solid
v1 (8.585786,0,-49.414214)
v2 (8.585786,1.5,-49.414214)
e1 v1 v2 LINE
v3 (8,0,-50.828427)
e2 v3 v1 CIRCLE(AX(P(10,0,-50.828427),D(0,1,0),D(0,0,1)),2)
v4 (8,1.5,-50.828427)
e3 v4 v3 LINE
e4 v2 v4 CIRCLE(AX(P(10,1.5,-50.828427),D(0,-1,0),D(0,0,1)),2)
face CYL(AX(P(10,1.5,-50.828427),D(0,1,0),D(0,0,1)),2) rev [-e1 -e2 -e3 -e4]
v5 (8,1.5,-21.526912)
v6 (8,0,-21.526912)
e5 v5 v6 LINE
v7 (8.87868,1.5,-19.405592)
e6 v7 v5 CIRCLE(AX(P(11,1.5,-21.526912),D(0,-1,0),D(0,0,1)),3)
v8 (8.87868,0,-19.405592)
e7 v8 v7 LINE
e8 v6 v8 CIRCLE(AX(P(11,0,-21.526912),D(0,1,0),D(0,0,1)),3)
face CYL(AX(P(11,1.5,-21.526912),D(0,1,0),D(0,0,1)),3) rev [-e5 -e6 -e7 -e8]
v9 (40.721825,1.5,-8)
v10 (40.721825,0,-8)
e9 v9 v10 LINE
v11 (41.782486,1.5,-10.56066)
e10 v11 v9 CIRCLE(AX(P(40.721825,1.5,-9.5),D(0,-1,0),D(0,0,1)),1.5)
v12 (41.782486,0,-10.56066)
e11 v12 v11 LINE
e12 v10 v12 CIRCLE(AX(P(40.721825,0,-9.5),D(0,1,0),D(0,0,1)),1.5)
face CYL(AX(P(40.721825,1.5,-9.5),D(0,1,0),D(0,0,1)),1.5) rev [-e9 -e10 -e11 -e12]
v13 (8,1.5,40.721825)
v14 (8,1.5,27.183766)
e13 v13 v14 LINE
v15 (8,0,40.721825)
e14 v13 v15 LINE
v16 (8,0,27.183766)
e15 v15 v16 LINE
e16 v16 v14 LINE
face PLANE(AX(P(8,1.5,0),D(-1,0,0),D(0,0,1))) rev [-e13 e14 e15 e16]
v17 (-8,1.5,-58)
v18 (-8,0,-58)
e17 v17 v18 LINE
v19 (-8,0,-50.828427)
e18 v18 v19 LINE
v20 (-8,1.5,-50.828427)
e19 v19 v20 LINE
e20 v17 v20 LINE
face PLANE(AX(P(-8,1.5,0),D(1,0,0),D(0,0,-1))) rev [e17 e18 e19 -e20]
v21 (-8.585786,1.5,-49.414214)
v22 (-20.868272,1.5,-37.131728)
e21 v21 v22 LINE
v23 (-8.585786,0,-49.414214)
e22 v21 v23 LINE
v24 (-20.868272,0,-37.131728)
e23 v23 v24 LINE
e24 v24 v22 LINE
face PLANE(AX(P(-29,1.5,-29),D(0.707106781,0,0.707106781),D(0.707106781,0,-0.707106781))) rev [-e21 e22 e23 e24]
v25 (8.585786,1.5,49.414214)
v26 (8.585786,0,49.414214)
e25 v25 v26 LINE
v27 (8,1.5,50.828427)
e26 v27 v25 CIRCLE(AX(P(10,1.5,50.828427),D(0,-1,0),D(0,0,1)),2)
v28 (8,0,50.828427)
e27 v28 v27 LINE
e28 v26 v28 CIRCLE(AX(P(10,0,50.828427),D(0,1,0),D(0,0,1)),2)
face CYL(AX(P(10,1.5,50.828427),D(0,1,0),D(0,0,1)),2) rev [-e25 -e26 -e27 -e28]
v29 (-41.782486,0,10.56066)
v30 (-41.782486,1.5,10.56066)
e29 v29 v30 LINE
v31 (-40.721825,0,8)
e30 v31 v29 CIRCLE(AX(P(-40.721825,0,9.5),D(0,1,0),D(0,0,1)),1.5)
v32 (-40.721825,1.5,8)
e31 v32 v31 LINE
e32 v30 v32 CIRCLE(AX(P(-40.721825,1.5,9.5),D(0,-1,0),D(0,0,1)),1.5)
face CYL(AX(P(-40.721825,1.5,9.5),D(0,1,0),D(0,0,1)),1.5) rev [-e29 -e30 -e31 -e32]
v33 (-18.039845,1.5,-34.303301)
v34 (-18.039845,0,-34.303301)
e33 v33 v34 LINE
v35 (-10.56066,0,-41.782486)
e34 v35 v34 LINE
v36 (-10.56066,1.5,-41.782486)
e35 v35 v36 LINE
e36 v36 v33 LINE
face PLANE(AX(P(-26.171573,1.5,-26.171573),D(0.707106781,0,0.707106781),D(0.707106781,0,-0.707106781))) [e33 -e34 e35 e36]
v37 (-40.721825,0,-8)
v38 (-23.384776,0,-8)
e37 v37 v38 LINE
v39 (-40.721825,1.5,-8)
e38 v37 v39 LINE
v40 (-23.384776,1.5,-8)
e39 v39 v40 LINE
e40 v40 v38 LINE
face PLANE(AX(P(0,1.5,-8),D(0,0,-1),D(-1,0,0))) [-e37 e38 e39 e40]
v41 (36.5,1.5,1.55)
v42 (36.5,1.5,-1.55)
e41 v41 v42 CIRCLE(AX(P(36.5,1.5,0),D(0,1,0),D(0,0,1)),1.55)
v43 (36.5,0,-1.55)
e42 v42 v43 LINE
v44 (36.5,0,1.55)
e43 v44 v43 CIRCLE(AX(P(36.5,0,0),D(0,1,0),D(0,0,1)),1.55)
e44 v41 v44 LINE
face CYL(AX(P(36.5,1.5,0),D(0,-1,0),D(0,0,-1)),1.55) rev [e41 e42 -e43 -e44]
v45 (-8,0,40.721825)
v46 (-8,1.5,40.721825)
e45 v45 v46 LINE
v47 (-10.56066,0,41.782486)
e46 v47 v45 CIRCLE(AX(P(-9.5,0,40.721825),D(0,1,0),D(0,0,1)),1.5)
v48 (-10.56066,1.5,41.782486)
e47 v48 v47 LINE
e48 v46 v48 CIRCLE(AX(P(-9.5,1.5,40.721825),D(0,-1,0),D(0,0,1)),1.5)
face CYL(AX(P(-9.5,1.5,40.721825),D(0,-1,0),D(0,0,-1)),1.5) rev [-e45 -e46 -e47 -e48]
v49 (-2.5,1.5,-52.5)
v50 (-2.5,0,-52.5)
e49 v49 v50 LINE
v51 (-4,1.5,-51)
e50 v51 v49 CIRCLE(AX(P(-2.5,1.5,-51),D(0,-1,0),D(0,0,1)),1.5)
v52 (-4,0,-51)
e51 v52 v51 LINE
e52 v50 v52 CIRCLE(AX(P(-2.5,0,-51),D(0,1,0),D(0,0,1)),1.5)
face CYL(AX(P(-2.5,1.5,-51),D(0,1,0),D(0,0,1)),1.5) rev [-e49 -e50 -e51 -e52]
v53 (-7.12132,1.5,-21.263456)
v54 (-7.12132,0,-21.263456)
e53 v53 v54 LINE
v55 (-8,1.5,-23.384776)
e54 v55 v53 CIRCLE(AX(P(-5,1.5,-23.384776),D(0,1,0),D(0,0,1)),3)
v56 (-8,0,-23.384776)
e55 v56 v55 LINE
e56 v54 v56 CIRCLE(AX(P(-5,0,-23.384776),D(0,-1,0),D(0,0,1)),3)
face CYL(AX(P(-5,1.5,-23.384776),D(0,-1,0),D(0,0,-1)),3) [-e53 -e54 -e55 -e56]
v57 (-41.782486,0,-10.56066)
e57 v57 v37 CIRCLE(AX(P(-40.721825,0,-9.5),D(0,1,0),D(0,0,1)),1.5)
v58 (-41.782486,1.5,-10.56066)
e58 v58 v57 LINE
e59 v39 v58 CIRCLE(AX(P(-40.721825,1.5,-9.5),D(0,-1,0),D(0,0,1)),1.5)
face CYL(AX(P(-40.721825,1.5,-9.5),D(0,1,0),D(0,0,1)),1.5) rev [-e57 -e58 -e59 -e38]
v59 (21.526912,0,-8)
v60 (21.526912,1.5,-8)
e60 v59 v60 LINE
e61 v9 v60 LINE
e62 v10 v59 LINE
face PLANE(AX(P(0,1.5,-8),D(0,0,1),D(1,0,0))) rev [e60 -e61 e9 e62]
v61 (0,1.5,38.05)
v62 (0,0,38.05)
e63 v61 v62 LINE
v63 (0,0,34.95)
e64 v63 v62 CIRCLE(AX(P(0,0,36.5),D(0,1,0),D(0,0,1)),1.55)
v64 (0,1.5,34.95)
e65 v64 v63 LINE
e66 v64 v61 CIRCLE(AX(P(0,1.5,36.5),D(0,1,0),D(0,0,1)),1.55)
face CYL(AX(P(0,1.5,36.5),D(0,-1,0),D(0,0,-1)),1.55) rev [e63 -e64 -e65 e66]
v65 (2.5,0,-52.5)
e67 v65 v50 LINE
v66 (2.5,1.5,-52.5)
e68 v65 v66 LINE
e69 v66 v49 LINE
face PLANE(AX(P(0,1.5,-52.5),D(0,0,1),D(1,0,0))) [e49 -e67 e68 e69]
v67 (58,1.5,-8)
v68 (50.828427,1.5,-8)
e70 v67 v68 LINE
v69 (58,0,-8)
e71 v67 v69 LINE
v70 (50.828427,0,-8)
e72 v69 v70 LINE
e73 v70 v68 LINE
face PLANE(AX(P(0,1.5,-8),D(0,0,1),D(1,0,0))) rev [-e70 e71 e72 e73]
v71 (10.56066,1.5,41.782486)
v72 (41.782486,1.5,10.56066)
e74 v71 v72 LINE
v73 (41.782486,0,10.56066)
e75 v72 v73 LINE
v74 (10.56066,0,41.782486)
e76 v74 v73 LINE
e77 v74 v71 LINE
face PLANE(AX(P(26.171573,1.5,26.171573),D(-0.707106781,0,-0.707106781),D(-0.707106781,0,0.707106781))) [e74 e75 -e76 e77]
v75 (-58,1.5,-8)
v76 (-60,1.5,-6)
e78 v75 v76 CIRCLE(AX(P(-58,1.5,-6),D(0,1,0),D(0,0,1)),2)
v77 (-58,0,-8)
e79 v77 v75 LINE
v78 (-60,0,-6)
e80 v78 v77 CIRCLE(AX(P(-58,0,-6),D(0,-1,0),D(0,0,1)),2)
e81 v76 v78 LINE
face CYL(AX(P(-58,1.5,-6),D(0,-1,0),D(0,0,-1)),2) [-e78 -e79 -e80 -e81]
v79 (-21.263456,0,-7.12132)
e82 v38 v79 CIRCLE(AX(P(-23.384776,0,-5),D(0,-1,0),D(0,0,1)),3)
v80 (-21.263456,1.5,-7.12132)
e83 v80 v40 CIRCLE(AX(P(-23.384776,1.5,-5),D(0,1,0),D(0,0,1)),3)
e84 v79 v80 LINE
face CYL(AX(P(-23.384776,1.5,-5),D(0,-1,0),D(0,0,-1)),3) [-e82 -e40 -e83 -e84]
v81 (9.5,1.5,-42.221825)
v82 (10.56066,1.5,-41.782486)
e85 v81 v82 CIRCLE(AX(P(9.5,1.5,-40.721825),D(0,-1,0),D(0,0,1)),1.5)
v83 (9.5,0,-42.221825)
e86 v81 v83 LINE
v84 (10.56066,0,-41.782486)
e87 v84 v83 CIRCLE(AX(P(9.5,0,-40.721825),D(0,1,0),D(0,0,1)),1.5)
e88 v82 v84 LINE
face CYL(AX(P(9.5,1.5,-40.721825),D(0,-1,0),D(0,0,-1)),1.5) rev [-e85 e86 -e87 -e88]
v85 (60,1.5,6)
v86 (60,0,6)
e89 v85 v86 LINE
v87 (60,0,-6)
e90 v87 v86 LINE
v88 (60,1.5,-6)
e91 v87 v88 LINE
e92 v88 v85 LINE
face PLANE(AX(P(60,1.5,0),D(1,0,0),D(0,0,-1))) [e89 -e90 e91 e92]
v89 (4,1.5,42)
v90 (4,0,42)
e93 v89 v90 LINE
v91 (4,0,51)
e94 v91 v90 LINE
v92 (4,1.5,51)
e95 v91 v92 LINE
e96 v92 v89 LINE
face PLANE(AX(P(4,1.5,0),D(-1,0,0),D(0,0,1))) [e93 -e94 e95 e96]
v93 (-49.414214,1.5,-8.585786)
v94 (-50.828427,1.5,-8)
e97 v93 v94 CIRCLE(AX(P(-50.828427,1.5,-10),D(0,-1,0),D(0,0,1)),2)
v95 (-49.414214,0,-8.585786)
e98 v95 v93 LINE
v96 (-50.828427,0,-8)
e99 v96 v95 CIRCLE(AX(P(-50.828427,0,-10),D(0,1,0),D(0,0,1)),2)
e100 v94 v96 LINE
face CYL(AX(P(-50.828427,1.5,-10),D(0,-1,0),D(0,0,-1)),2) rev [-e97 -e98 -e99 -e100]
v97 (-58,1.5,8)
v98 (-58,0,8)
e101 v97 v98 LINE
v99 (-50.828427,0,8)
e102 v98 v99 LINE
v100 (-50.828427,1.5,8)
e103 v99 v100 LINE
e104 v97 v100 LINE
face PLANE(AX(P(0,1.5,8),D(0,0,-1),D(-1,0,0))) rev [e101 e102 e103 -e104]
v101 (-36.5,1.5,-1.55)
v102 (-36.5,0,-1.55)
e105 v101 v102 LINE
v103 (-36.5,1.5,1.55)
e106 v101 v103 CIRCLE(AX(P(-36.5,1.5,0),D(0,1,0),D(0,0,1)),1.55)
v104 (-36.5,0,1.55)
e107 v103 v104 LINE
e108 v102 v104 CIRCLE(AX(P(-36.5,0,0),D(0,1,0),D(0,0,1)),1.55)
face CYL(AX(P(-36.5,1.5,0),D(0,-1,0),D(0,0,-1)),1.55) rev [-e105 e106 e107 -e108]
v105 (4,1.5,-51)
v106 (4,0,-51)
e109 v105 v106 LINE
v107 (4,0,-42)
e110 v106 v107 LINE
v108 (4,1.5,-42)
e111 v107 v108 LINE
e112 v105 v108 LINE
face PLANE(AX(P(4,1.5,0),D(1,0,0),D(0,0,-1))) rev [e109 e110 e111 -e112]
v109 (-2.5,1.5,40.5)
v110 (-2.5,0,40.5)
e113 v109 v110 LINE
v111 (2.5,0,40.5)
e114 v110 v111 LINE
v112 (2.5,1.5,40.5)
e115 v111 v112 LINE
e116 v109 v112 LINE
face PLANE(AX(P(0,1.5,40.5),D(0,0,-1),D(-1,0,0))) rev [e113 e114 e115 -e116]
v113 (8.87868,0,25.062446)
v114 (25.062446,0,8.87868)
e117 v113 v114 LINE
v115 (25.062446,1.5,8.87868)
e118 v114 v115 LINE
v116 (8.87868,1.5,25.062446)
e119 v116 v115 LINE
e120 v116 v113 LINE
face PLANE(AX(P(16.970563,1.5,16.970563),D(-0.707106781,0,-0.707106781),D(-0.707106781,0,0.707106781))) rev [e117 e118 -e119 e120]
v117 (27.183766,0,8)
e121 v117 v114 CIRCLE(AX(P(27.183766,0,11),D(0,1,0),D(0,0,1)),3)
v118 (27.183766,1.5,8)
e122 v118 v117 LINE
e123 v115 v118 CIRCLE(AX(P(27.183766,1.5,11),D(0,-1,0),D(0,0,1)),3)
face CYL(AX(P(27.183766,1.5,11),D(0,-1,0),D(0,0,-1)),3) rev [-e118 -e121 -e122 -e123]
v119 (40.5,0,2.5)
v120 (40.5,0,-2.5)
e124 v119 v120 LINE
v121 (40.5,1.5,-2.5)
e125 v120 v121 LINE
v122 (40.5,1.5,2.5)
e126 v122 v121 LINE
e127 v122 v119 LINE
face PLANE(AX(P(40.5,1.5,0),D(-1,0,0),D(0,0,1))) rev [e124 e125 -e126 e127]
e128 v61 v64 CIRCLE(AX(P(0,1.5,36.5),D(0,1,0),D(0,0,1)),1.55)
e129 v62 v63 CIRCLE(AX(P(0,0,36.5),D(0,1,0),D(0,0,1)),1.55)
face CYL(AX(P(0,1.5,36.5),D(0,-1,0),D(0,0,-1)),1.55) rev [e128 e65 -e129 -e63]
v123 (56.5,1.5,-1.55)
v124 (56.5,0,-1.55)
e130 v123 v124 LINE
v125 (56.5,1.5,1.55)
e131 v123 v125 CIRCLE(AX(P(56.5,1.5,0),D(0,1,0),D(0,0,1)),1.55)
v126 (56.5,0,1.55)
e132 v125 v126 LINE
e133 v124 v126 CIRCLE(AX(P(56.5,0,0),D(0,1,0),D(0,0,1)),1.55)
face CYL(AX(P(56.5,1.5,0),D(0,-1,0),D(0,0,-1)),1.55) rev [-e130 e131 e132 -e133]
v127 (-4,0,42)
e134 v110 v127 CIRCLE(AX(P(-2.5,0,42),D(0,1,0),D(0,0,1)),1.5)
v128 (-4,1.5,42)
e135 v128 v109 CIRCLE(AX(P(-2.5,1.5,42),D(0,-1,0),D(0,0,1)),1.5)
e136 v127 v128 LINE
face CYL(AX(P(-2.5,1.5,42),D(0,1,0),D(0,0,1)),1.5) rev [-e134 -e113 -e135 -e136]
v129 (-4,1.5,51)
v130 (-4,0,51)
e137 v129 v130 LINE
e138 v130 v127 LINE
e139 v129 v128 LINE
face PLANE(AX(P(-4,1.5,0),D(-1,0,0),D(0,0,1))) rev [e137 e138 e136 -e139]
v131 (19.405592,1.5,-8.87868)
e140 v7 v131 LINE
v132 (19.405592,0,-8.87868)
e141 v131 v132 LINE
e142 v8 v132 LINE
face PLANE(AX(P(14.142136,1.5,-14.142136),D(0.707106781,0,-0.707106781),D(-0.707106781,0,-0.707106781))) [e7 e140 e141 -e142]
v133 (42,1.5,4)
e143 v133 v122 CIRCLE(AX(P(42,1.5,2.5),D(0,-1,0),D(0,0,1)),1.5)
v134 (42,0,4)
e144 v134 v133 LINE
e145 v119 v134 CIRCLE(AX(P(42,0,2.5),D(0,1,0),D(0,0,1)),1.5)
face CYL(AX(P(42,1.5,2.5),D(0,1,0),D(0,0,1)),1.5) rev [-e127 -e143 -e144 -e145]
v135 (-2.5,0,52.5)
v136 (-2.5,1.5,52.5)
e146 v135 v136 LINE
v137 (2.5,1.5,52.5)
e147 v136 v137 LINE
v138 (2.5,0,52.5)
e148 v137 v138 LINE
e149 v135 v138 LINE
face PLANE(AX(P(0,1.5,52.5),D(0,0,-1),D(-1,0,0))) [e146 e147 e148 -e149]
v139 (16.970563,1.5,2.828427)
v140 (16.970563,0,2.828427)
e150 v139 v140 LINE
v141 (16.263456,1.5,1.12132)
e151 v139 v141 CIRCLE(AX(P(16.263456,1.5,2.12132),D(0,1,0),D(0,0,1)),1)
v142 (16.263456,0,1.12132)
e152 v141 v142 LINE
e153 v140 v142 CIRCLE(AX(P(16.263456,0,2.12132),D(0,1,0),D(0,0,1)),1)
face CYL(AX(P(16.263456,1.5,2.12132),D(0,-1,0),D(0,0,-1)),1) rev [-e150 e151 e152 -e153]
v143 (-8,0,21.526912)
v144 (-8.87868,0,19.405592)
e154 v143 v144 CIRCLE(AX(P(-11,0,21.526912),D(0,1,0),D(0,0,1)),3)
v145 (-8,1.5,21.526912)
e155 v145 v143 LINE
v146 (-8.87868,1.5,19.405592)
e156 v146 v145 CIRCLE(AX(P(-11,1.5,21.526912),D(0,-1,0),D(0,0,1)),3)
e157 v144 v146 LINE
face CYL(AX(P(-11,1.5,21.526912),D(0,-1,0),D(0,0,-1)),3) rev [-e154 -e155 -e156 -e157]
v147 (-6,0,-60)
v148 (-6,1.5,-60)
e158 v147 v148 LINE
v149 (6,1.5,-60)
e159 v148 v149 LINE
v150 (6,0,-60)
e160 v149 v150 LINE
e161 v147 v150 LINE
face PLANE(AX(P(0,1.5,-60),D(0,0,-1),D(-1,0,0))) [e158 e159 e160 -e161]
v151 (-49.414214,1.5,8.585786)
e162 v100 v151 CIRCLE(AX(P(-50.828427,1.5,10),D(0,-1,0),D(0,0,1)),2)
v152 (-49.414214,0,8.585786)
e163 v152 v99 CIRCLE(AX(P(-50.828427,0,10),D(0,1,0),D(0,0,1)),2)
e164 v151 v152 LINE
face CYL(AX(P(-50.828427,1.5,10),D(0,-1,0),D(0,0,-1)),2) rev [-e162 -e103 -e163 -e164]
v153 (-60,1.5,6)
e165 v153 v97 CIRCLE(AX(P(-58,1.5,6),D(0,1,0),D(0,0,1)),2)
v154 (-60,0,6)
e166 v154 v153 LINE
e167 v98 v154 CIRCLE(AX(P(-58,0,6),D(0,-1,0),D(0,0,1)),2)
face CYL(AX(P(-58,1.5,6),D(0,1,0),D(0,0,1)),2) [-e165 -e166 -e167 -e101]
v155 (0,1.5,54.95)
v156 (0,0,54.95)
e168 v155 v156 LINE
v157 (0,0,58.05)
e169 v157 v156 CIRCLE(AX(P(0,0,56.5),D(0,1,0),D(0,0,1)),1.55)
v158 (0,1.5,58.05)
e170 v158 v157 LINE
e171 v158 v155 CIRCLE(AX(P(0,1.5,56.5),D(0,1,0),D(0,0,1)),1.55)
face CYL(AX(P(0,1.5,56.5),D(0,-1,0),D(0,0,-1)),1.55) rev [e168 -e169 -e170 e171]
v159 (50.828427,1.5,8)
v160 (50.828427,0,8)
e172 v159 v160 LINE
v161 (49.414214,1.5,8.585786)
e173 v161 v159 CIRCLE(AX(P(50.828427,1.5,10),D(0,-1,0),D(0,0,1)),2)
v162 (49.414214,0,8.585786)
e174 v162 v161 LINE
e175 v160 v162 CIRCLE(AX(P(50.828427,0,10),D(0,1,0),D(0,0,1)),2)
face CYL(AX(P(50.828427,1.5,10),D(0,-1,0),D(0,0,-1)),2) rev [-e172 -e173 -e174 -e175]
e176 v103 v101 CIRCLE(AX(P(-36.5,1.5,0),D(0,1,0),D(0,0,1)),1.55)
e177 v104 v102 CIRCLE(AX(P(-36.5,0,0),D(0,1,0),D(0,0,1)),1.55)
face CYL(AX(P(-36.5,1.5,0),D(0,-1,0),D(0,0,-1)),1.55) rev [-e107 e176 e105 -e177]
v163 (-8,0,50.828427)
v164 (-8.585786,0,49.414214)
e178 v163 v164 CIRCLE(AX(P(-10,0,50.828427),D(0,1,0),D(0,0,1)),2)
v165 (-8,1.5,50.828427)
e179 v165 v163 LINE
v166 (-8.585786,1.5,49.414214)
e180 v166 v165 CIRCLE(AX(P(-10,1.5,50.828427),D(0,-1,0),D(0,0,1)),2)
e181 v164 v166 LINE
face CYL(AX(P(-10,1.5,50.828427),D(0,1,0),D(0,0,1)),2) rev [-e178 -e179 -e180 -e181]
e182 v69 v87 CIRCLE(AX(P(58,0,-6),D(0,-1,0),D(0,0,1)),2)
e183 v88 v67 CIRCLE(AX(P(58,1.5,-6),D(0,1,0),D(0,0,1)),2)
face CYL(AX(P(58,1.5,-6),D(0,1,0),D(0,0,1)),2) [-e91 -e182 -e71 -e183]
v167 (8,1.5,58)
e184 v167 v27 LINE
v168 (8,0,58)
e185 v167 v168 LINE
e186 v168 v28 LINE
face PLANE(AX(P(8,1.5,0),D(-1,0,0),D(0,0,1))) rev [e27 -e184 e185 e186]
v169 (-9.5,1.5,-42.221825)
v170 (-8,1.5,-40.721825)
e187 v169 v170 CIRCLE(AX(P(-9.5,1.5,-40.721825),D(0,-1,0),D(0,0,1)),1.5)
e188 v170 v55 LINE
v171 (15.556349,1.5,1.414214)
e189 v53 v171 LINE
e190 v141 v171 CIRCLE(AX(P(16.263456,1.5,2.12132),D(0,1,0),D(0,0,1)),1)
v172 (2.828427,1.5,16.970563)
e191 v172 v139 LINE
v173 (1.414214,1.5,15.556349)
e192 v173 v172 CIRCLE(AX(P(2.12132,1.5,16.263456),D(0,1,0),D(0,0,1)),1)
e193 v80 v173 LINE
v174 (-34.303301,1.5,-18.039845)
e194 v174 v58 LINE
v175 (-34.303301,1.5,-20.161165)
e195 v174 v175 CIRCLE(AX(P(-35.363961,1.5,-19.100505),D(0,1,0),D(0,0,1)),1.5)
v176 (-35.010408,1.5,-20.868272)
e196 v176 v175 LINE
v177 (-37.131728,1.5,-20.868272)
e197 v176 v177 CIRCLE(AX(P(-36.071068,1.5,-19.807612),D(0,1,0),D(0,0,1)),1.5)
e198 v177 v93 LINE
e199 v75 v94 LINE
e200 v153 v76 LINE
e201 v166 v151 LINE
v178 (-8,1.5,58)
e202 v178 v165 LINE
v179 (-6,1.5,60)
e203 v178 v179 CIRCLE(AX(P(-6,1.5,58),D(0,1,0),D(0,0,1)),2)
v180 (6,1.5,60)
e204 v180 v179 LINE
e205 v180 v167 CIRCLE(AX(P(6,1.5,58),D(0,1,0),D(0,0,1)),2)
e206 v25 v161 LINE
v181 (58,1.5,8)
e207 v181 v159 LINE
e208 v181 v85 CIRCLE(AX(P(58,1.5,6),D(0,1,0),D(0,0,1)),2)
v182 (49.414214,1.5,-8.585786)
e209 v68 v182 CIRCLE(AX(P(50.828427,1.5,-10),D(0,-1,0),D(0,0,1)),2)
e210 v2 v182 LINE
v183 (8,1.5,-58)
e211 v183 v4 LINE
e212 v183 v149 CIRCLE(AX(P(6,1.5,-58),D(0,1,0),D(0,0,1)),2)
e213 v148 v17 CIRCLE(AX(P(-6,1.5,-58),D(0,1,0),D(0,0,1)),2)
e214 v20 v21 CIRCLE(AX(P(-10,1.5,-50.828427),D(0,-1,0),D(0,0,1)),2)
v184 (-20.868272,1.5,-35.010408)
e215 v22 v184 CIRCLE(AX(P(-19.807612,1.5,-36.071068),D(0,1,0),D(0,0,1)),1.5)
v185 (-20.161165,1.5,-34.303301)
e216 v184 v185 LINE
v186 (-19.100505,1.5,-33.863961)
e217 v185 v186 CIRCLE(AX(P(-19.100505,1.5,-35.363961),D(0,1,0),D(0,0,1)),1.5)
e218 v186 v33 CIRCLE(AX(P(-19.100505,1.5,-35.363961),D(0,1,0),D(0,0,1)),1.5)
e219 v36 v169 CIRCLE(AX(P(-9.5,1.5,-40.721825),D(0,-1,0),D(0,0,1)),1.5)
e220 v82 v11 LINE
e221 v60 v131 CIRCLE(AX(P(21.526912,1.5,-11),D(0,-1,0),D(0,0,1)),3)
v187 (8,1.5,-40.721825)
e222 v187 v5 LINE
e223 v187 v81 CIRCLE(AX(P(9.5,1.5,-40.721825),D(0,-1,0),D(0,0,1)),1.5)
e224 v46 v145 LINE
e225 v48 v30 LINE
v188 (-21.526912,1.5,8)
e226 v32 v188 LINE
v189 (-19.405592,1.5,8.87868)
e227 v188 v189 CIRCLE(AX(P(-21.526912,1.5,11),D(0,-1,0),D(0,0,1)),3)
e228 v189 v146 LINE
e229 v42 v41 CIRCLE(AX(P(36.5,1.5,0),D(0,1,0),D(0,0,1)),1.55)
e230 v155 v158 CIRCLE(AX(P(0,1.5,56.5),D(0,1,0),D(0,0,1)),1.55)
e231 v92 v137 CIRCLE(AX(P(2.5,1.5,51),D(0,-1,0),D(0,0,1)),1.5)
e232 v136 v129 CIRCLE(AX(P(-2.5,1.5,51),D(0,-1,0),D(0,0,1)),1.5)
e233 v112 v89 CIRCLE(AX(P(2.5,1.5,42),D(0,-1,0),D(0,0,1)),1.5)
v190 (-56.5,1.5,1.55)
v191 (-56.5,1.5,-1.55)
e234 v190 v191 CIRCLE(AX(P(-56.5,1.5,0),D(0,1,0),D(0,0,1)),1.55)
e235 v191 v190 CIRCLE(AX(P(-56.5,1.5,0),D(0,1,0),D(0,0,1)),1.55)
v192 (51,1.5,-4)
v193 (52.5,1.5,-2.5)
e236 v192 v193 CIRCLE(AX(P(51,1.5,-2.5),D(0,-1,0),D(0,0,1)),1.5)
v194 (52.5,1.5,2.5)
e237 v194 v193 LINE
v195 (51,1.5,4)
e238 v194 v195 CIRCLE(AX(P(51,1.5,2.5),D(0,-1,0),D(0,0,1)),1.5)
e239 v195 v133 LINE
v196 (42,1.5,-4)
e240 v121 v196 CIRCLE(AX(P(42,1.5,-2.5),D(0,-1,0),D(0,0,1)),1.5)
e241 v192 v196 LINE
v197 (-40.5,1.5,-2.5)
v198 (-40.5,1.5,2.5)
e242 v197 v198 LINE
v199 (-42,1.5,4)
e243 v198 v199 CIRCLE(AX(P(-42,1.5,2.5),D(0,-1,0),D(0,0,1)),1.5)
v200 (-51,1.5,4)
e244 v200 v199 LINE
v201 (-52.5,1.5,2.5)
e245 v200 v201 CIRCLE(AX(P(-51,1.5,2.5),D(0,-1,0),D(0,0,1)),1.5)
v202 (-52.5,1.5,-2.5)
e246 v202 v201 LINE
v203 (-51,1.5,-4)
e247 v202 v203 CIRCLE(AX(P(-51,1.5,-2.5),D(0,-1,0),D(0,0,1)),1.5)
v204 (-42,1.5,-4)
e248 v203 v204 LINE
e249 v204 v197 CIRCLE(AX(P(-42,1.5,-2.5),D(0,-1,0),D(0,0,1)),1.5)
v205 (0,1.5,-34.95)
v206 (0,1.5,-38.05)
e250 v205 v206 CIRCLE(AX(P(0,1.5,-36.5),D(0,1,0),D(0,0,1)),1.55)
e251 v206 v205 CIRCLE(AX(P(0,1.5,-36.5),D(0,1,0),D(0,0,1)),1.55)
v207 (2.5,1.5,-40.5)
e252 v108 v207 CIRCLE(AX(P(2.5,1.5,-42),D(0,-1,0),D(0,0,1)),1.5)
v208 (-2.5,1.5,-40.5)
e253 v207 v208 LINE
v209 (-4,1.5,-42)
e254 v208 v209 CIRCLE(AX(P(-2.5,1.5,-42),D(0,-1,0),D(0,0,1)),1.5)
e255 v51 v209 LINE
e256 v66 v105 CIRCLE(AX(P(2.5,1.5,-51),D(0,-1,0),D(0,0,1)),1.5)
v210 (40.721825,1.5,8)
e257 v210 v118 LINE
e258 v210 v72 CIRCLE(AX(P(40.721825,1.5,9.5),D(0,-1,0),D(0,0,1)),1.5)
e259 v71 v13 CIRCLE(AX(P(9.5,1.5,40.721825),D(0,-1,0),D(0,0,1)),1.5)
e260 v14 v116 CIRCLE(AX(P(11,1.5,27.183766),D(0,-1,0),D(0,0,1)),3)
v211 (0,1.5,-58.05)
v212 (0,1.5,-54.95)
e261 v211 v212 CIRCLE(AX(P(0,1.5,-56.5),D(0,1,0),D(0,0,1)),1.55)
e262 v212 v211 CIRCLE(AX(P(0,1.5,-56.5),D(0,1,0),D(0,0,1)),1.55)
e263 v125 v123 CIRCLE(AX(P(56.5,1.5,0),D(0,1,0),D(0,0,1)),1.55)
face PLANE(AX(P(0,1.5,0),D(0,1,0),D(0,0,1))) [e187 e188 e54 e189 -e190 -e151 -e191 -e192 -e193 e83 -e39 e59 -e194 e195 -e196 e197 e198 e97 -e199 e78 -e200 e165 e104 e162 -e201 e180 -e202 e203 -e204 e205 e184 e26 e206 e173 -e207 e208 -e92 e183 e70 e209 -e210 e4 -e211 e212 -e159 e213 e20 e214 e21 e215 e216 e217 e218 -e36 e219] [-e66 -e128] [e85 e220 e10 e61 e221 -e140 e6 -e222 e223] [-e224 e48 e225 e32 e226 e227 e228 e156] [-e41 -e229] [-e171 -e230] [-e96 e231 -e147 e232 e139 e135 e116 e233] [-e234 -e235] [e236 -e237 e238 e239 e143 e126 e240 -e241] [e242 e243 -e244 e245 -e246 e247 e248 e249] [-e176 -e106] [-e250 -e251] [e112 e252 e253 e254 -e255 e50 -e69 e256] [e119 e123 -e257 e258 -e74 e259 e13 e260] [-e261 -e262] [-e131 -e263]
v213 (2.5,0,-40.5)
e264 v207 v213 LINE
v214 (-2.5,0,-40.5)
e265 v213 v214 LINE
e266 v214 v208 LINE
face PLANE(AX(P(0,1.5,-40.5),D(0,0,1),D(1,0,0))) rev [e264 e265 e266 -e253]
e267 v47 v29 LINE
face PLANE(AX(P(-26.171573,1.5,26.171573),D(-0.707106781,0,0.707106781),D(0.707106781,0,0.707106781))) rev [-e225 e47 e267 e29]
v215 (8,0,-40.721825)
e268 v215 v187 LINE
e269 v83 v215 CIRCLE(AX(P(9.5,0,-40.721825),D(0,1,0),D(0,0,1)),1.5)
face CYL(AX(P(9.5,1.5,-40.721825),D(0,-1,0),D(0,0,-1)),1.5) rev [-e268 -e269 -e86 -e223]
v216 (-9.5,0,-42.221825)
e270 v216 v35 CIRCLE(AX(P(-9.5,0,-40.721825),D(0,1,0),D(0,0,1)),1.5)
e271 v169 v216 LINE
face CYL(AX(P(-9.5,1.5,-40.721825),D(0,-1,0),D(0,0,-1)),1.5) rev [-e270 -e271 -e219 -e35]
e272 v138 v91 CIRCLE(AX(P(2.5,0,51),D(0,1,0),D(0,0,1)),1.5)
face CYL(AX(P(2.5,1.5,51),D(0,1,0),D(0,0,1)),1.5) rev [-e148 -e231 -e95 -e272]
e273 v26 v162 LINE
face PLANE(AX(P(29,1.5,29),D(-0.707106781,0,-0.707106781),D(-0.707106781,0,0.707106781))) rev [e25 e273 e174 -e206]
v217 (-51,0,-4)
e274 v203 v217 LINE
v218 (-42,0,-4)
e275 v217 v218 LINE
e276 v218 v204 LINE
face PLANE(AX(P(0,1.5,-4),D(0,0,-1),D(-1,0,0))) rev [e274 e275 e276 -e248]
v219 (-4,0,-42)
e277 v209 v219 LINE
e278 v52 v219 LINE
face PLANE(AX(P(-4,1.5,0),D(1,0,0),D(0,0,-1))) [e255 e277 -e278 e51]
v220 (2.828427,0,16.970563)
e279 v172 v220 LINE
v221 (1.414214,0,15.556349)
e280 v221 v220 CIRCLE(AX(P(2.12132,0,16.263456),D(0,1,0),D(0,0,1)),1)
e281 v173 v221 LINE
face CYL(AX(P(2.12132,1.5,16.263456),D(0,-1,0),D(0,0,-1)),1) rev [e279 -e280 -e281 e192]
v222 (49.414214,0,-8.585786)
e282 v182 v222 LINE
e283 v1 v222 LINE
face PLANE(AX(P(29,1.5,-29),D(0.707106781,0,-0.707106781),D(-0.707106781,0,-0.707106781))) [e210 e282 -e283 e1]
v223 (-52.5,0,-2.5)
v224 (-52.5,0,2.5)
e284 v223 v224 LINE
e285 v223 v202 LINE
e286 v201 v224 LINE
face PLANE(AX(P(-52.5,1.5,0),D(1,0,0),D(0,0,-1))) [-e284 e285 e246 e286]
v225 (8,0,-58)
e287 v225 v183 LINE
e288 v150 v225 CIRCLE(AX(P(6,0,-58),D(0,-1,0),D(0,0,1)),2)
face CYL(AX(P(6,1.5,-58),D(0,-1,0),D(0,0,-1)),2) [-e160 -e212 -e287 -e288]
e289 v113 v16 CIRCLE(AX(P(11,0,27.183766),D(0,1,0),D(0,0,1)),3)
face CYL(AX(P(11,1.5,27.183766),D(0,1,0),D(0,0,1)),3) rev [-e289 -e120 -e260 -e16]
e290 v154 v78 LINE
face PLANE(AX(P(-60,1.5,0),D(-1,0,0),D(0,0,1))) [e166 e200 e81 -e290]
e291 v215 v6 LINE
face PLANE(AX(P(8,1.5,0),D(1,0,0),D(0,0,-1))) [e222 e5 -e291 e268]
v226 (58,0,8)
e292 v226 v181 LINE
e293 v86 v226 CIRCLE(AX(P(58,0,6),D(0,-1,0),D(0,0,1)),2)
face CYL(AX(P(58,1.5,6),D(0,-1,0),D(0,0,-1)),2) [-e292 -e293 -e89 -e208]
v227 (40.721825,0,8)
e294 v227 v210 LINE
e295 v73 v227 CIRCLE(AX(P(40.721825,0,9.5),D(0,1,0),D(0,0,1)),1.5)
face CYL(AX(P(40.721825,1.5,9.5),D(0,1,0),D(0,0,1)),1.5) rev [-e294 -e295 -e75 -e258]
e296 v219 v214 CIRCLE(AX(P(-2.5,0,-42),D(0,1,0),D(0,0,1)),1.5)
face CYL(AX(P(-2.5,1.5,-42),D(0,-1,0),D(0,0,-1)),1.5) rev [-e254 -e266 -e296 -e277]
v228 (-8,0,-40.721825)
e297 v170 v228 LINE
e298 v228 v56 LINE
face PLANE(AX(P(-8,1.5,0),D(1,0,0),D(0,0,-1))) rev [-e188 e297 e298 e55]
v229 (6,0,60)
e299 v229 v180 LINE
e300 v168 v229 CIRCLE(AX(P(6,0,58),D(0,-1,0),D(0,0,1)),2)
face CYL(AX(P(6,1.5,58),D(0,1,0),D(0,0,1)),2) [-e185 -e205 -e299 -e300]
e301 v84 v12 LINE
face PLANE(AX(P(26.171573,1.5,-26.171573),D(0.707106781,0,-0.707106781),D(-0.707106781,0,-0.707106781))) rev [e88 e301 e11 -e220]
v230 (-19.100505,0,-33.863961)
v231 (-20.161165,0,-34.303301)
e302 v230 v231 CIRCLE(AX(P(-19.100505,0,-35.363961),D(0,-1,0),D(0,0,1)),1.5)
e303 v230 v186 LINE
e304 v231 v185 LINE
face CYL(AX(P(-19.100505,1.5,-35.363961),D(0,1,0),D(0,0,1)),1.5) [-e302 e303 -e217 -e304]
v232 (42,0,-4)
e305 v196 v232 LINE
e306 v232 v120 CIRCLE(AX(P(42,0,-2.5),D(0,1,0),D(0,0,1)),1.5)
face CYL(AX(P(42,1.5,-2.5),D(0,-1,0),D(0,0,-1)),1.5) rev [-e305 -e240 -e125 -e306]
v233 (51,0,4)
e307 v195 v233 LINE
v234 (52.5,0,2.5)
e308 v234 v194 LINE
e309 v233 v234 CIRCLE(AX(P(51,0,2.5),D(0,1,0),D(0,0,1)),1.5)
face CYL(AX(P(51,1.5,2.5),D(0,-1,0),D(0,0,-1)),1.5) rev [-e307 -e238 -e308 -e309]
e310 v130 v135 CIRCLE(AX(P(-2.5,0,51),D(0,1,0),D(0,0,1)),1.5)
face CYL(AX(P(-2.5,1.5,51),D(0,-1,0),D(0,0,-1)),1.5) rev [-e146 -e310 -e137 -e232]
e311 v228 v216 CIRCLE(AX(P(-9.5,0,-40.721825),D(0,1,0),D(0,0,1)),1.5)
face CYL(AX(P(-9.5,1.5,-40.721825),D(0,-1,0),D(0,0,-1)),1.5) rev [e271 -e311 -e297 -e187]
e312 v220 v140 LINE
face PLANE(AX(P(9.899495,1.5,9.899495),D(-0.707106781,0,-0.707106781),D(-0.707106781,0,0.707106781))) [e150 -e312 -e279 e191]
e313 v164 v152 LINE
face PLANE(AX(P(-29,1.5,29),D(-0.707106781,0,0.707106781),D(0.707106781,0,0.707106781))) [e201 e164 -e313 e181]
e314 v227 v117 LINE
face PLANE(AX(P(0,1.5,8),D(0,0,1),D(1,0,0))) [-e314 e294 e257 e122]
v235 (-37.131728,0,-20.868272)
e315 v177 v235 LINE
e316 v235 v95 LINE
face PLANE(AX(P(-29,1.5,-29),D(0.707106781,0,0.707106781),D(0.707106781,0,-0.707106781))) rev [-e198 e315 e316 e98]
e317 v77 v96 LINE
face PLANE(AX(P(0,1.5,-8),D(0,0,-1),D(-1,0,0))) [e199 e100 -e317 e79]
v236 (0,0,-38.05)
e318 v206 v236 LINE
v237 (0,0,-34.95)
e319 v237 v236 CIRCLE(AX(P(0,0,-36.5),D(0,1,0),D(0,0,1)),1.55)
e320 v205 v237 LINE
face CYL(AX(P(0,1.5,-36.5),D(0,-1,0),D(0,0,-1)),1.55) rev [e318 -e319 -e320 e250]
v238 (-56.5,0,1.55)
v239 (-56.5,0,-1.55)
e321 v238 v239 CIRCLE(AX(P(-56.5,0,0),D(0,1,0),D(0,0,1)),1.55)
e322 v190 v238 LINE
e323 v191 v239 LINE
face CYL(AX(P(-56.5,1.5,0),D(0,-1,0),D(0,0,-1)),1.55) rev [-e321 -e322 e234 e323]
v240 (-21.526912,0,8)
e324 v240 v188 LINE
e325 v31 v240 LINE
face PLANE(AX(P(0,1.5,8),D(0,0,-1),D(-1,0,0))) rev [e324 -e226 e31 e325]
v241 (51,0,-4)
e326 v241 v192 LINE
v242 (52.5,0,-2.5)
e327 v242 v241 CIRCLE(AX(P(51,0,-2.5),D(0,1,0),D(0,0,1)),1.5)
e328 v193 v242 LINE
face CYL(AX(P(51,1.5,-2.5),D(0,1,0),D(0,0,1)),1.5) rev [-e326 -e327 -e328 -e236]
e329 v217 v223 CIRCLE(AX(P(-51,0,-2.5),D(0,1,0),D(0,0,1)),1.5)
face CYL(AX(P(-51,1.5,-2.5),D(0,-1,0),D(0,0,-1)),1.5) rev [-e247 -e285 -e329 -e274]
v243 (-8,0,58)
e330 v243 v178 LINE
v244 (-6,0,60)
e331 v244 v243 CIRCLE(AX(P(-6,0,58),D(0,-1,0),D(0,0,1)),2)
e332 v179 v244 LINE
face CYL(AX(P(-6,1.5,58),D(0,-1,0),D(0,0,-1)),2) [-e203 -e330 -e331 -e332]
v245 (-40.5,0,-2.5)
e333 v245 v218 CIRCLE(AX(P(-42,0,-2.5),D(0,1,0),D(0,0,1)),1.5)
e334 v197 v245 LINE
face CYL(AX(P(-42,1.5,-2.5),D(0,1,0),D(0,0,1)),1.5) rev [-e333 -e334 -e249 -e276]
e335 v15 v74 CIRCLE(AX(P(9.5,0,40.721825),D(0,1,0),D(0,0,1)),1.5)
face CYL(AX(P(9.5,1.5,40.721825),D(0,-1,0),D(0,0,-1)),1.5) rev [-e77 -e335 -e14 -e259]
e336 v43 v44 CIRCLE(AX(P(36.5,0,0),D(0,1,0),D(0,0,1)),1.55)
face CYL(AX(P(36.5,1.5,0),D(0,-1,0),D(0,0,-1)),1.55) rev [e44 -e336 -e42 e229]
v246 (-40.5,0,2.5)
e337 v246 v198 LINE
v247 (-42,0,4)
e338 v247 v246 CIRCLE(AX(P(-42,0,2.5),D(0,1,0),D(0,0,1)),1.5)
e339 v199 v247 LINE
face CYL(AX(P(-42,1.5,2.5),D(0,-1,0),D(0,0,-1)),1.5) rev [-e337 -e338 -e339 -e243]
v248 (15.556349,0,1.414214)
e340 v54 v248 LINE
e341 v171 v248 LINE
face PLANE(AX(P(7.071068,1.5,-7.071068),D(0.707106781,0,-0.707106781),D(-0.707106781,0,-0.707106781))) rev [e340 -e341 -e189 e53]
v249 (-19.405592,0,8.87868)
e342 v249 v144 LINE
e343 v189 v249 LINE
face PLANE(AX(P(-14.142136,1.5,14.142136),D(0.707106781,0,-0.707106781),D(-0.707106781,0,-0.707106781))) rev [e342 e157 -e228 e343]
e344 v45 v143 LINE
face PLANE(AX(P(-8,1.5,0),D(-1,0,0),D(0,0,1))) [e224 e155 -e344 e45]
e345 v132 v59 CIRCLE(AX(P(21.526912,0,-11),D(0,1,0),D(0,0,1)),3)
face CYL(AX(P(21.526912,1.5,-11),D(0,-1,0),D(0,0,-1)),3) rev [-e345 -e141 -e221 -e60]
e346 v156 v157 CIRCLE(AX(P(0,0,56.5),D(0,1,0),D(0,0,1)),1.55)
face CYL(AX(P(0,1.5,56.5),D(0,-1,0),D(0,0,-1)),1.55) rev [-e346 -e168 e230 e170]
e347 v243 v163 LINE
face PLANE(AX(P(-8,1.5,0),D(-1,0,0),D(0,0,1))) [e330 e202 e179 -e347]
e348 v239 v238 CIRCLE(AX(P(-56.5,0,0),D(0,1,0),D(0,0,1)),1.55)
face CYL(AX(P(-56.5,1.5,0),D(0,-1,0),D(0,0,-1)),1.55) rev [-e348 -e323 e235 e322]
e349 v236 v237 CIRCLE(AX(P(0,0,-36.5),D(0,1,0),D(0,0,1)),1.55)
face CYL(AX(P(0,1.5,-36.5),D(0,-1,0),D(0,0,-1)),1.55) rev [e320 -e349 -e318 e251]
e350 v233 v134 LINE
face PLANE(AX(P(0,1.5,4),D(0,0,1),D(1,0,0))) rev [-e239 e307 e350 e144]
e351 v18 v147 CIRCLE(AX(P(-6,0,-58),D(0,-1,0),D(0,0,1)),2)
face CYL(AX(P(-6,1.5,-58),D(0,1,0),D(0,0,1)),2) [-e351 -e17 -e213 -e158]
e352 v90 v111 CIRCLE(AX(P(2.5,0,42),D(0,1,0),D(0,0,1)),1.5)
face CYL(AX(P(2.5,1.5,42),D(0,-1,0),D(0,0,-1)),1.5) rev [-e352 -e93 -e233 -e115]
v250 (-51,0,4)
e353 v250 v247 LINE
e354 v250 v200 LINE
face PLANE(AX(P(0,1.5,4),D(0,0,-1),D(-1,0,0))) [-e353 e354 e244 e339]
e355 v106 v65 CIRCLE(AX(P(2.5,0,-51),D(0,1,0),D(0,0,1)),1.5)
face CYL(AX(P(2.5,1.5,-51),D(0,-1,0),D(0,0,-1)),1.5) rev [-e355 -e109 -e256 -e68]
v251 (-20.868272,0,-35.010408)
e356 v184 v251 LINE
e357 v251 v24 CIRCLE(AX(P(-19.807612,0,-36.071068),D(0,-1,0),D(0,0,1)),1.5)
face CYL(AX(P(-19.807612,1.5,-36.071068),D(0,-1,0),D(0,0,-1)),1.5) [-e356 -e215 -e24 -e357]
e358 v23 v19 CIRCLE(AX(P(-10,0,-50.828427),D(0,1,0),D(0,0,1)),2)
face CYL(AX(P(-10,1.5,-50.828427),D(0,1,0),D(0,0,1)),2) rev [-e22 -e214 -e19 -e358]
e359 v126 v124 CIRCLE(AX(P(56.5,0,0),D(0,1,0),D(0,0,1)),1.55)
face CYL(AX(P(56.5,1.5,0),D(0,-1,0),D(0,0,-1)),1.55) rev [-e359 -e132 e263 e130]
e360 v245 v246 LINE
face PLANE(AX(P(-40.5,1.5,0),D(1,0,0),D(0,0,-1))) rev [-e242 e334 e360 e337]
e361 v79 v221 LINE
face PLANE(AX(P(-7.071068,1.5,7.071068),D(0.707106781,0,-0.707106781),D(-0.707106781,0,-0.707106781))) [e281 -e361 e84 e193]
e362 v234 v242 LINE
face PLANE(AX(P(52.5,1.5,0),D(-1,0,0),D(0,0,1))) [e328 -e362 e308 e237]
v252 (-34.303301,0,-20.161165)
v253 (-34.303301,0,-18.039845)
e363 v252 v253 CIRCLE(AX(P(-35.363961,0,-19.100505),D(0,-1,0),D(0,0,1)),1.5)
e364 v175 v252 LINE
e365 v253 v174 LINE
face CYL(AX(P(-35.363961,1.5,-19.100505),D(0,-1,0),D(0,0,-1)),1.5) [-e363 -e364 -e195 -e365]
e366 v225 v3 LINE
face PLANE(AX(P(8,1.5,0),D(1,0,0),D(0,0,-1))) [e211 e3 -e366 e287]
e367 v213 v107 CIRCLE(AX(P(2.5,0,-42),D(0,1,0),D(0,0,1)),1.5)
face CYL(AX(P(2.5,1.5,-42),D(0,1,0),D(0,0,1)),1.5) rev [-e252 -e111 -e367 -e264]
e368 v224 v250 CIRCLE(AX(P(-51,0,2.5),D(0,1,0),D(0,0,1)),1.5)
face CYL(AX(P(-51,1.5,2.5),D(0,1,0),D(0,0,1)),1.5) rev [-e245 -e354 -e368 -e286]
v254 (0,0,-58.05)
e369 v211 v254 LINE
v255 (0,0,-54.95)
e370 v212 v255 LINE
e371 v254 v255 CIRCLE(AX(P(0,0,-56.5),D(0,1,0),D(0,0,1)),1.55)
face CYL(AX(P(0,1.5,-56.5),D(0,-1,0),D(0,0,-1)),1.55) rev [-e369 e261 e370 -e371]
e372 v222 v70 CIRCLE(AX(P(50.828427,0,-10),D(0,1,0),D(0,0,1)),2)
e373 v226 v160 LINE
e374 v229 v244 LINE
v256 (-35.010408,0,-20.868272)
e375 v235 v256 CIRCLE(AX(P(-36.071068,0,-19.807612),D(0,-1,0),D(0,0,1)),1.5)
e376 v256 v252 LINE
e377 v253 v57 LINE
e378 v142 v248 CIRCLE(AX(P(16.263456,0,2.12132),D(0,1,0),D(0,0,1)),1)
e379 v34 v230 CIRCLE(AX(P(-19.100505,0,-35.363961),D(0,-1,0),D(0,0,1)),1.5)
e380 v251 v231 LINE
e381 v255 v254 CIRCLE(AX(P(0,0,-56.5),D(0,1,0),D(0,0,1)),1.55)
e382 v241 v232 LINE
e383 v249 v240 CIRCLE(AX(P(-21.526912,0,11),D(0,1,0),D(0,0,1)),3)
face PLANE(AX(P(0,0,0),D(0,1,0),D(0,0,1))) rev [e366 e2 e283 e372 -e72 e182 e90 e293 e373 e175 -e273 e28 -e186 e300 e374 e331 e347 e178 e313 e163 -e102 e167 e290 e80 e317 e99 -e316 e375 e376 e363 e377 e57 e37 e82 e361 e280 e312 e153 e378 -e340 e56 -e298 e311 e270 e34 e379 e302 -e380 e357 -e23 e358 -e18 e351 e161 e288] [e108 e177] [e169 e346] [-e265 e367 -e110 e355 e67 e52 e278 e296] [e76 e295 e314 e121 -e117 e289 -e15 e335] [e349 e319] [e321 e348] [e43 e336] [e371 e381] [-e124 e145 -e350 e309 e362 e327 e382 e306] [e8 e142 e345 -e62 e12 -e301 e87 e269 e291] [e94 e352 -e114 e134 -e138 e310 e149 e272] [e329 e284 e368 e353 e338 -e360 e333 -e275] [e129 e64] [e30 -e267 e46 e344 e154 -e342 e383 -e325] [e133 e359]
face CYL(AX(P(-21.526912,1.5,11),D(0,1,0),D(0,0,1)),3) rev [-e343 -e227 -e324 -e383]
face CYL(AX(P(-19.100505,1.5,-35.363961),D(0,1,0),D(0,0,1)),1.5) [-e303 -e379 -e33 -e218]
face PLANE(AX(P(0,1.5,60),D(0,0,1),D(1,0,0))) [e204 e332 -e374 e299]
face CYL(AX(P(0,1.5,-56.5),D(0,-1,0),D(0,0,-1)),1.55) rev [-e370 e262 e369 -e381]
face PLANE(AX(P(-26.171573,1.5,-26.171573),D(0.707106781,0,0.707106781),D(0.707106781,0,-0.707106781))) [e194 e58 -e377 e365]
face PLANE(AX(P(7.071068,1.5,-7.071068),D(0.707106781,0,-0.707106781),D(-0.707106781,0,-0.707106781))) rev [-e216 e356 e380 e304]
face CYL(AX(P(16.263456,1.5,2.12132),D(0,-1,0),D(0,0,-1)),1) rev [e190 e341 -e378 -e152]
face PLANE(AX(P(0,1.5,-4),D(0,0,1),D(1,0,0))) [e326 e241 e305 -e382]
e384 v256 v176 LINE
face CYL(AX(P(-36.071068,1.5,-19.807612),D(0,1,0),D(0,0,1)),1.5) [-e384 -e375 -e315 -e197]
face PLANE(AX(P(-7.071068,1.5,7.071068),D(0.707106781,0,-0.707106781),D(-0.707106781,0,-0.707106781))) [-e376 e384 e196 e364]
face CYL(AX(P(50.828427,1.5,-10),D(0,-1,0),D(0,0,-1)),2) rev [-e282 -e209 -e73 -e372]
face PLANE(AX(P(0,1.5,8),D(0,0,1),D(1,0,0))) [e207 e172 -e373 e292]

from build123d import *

# Parameters (mm, degrees)
SKETCH_1_R      = 1.55
SKETCH_1_W      = 8
SKETCH_1_H      = 12
SKETCH_1_W_2    = 12
SKETCH_1_H_2    = 8
EXTRUDE_1_DEPTH = 1.5
F_2MM_R         = 2
F_1_5MM_R       = 1.5
F_3MM_R         = 3


with BuildPart() as part:
    # 草图1 → 凸台-拉伸1 (new body)
    with BuildSketch(Plane(origin=(0, 0, 0), x_dir=(1, 0, 0), z_dir=(0, 1, 0))):
        with BuildLine():
            Line((8, 60), (-8, 60))
            Line((-8, 60), (-8, 50))
            Line((-8, 50), (-21.928932188, 36.071067812))
            Line((-21.928932188, 36.071067812), (-19.100505063, 33.242640687))
            Line((-19.100505063, 33.242640687), (-8, 44.343145751))
            Line((-8, 44.343145751), (-8, 22.142135624))
            Line((-8, 22.142135624), (15.556349186, -1.414213562))
            ThreePointArc((15.556349186, -1.414213562), (16.970562748, -1.414213562), (16.970562748, -2.828427125))
            Line((16.970562748, -2.828427125), (2.828427125, -16.970562748))
            ThreePointArc((2.828427125, -16.970562748), (1.414213562, -16.970562748), (1.414213562, -15.556349186))
            Line((1.414213562, -15.556349186), (-22.142135624, 8))
            Line((-22.142135624, 8), (-44.343145751, 8))
            Line((-44.343145751, 8), (-33.242640687, 19.100505063))
            Line((-33.242640687, 19.100505063), (-36.071067812, 21.928932188))
            Line((-36.071067812, 21.928932188), (-50, 8))
            Line((-50, 8), (-60, 8))
            Line((-60, 8), (-60, -8))
            Line((-60, -8), (-50, -8))
            Line((-50, -8), (-8, -50))
            Line((-8, -50), (-8, -60))
            Line((-8, -60), (8, -60))
            Line((8, -60), (8, -50))
            Line((8, -50), (50, -8))
            Line((50, -8), (60, -8))
            Line((60, -8), (60, 8))
            Line((60, 8), (50, 8))
            Line((50, 8), (8, 50))
            Line((8, 50), (8, 60))
        make_face()
        Polygon((-44.343145751, -8), (-20.284271247, -8), (-8, -20.284271247), (-8, -44.343145751), align=None, mode=Mode.SUBTRACT)
        Polygon((8, -44.343145751), (8, -25.941125497), (25.941125497, -8), (44.343145751, -8), align=None, mode=Mode.SUBTRACT)
        Polygon((44.343145751, 8), (20.284271247, 8), (8, 20.284271247), (8, 44.343145751), align=None, mode=Mode.SUBTRACT)
        with Locations(Location((-36.5, 0, 0), (0, 0, 270))):
            Circle(SKETCH_1_R, mode=Mode.SUBTRACT)
        with Locations(Location((0, -56.5, 0), (0, 0, 270))):
            Circle(SKETCH_1_R, mode=Mode.SUBTRACT)
        with Locations((0, -46.5)):
            Rectangle(SKETCH_1_W, SKETCH_1_H, mode=Mode.SUBTRACT)
        with Locations(Location((0, -36.5, 0), (0, 0, 270))):
            Circle(SKETCH_1_R, mode=Mode.SUBTRACT)
        with Locations(Location((-56.5, 0, 0), (0, 0, 270))):
            Circle(SKETCH_1_R, mode=Mode.SUBTRACT)
        with Locations((-46.5, 0)):
            Rectangle(SKETCH_1_W_2, SKETCH_1_H_2, mode=Mode.SUBTRACT)
        with Locations(Location((36.5, 0, 0), (0, 0, 270))):
            Circle(SKETCH_1_R, mode=Mode.SUBTRACT)
        with Locations((46.5, 0)):
            Rectangle(SKETCH_1_W_2, SKETCH_1_H_2, mode=Mode.SUBTRACT)
        with Locations(Location((56.5, 0, 0), (0, 0, 270))):
            Circle(SKETCH_1_R, mode=Mode.SUBTRACT)
        with Locations(Location((0, 36.5, 0), (0, 0, 270))):
            Circle(SKETCH_1_R, mode=Mode.SUBTRACT)
        with Locations((0, 46.5)):
            Rectangle(SKETCH_1_W, SKETCH_1_H, mode=Mode.SUBTRACT)
        with Locations(Location((0, 56.5, 0), (0, 0, 270))):
            Circle(SKETCH_1_R, mode=Mode.SUBTRACT)
    extrude(amount=EXTRUDE_1_DEPTH)

    # 2mm
    f_2mm_edges = [part.edges().sort_by_distance(p)[0] for p in [
        (-60, 0.75, 8),
        (-60, 0.75, -8),
        (-50, 0.75, -8),
        (-8, 0.75, -50),
        (-8, 0.75, -60),
        (8, 0.75, -60),
        (8, 0.75, -50),
        (50, 0.75, -8),
        (60, 0.75, -8),
        (60, 0.75, 8),
        (50, 0.75, 8),
        (8, 0.75, 50),
        (8, 0.75, 60),
        (-8, 0.75, 60),
        (-8, 0.75, 50),
        (-50, 0.75, 8),
    ]]
    fillet(f_2mm_edges, radius=F_2MM_R)

    # 1.5mm
    f_1_5mm_edges = [part.edges().sort_by_distance(p)[0] for p in [
        (-4, 0.75, 52.5),
        (4, 0.75, 52.5),
        (4, 0.75, 40.5),
        (-4, 0.75, 40.5),
        (52.5, 0.75, 4),
        (52.5, 0.75, -4),
        (40.5, 0.75, -4),
        (40.5, 0.75, 4),
        (4, 0.75, -52.5),
        (-4, 0.75, -52.5),
        (-4, 0.75, -40.5),
        (4, 0.75, -40.5),
        (-52.5, 0.75, -4),
        (-52.5, 0.75, 4),
        (-40.5, 0.75, 4),
        (-40.5, 0.75, -4),
        (8, 0.75, -44.343145751),
        (44.343145751, 0.75, -8),
        (44.343145751, 0.75, 8),
        (8, 0.75, 44.343145751),
        (-36.071067812, 0.75, -21.928932188),
        (-33.242640687, 0.75, -19.100505063),
        (-44.343145751, 0.75, -8),
        (-8, 0.75, -44.343145751),
        (-19.100505063, 0.75, -33.242640687),
        (-21.928932188, 0.75, -36.071067812),
        (-8, 0.75, 44.343145751),
        (-44.343145751, 0.75, 8),
    ]]
    fillet(f_1_5mm_edges, radius=F_1_5MM_R)

    # 3mm
    f_3mm_edges = [part.edges().sort_by_distance(p)[0] for p in [
        (8, 0.75, -20.284271247),
        (20.284271247, 0.75, -8),
        (25.941125497, 0.75, 8),
        (8, 0.75, 25.941125497),
        (-22.142135624, 0.75, -8),
        (-8, 0.75, -22.142135624),
        (-8, 0.75, 20.284271247),
        (-20.284271247, 0.75, 8),
    ]]
    fillet(f_3mm_edges, radius=F_3MM_R)


solid = part.part
